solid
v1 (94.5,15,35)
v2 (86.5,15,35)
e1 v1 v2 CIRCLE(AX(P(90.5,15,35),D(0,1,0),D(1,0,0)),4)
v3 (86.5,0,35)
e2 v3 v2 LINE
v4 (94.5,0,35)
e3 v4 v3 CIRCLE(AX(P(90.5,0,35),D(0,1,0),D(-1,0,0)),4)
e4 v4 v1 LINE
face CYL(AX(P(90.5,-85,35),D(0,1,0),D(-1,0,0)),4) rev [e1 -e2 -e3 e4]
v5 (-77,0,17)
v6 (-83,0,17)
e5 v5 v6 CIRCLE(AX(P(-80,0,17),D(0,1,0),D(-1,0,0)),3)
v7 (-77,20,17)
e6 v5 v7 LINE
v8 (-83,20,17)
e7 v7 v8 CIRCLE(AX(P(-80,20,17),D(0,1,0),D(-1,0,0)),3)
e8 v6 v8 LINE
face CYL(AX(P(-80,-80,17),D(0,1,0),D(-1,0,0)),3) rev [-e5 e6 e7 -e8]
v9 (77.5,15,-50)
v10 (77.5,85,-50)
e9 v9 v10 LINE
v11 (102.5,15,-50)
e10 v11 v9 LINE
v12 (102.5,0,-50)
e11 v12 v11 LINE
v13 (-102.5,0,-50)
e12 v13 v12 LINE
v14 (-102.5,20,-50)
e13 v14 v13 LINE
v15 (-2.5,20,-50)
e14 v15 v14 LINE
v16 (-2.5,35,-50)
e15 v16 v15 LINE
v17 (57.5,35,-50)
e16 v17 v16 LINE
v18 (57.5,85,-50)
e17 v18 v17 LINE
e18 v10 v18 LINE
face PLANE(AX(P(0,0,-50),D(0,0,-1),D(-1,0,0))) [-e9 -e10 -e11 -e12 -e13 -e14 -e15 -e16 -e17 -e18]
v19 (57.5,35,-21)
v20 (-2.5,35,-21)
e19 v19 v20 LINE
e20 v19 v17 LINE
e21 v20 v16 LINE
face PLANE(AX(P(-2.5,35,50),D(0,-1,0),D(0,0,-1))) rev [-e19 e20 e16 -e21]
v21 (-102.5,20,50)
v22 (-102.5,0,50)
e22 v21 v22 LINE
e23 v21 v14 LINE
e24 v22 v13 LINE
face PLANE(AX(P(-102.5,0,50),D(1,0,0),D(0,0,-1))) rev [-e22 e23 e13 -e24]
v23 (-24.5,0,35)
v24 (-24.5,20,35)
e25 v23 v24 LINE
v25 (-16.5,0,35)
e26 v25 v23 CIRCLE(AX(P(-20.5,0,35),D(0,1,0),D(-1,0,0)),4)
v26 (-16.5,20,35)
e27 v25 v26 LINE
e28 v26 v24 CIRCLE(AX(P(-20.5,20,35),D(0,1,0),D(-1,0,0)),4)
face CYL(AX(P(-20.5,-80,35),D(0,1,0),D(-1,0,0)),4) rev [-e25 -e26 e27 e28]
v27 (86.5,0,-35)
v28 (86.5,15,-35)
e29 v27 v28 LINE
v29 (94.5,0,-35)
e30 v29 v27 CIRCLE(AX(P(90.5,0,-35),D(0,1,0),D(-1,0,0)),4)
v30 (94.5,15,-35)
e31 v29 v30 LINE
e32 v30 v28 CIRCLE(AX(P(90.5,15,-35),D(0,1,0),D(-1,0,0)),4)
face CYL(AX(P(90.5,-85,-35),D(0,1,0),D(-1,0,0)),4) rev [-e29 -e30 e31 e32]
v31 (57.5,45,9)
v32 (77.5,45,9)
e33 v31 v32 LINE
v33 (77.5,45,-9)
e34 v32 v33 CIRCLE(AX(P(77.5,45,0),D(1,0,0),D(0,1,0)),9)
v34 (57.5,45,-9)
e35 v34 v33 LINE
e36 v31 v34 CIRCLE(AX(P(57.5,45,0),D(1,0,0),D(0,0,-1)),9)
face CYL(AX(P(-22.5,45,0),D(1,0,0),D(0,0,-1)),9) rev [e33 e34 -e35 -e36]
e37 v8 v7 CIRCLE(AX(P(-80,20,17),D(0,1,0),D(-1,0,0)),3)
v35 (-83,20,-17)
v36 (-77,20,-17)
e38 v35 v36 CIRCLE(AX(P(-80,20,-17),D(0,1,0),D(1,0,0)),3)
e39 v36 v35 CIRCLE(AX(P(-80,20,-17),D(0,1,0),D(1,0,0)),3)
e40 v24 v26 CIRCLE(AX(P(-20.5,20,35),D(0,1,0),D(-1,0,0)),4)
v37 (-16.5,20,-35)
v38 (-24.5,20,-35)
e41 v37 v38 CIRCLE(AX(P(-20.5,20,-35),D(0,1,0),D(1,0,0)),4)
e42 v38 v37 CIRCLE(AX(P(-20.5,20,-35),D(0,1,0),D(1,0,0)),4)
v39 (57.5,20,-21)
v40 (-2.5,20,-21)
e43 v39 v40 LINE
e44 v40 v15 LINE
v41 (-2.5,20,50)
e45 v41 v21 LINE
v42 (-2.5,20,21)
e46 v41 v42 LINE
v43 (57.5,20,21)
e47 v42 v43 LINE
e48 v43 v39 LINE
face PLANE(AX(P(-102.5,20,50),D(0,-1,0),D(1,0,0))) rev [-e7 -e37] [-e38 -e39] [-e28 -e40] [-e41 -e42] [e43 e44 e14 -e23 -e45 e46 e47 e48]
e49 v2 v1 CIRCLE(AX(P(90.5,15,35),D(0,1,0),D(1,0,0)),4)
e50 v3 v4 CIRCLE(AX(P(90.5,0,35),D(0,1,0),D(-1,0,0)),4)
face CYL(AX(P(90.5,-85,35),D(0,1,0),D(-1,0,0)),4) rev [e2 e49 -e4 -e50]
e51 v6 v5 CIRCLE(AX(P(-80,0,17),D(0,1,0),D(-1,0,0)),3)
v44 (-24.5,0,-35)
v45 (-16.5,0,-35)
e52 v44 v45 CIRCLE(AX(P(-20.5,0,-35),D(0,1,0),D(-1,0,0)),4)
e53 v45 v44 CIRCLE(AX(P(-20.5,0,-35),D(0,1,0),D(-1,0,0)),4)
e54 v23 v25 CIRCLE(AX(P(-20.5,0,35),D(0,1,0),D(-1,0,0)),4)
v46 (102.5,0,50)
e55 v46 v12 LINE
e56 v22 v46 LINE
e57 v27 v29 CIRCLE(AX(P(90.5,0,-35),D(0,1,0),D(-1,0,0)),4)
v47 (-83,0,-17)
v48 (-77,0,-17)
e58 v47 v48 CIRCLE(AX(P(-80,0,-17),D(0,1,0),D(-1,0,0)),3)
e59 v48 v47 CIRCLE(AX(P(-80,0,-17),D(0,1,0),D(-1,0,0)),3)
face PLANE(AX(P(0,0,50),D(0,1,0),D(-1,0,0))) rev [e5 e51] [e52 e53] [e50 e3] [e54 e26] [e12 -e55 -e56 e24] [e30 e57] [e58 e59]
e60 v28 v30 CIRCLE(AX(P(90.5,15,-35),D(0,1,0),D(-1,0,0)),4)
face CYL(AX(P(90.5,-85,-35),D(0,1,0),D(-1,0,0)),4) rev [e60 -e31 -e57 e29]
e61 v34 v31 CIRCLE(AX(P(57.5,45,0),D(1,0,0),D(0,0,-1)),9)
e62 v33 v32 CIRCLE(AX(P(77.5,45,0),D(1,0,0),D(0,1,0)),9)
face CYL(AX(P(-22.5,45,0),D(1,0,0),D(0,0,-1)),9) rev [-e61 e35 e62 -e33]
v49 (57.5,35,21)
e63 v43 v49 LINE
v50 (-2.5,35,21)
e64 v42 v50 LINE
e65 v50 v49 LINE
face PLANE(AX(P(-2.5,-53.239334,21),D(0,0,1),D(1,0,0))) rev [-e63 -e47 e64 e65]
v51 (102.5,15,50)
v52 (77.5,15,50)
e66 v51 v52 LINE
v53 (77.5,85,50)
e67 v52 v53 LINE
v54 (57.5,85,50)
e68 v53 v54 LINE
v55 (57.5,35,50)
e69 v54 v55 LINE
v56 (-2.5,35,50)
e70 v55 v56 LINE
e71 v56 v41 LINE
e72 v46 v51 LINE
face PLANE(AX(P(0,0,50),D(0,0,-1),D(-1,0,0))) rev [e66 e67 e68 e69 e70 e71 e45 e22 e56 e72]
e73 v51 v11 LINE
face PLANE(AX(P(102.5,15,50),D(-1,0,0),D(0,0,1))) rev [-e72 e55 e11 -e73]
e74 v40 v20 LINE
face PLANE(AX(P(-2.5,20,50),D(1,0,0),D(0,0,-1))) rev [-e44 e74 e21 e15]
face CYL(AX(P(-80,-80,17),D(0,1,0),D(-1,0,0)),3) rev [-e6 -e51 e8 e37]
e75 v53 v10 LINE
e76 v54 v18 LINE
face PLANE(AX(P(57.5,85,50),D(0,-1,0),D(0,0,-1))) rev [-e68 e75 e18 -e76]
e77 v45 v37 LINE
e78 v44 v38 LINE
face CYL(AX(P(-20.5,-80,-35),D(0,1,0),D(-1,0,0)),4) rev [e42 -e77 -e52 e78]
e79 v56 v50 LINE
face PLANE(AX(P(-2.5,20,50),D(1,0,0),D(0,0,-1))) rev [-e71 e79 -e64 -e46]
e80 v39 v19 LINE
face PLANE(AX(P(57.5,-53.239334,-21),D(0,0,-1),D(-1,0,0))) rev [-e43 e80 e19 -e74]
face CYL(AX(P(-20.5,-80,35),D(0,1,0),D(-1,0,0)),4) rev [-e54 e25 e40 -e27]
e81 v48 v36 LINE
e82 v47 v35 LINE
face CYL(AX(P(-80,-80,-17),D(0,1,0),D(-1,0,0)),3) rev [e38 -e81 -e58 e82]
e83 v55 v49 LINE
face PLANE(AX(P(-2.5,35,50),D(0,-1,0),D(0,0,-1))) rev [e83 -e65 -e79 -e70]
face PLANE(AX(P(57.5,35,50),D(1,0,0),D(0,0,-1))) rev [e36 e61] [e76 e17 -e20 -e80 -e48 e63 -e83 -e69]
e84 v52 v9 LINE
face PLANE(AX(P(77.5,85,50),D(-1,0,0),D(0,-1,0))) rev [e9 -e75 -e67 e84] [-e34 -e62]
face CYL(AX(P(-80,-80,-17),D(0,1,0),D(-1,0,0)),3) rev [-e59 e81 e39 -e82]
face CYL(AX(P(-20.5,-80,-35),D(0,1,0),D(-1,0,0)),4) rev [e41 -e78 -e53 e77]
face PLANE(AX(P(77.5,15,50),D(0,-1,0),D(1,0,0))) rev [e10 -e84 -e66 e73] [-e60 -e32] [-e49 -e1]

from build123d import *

# Parameters (mm, degrees)
BRACKET_BODY_DEPTH          = 50
BASE_HOLES_8_SET_A_SKETCH_R = 4
BASE_HOLES_8_SET_A_DEPTH    = 100
STEP_NOTCH_SKETCH_W         = 60
STEP_NOTCH_SKETCH_H         = 42
STEP_NOTCH_DEPTH            = 15
WEB_BORE_18_SKETCH_R        = 9
WEB_BORE_18_DEPTH           = 100
BASE_HOLES_8_SET_B_SKETCH_R = 4
BASE_HOLES_8_SET_B_DEPTH    = 100
BASE_HOLES_6_SKETCH_R       = 3
BASE_HOLES_6_DEPTH          = 100


with BuildPart() as part:
    # Bracket Profile Sketch → Bracket Body (new, symmetric)
    with BuildSketch(Plane.XY):
        Polygon((0, 0), (-102.5, 0), (-102.5, 20), (-2.5, 20), (-2.5, 35), (57.5, 35), (57.5, 85), (77.5, 85), (77.5, 15), (102.5, 15), (102.5, 0), align=None)
    extrude(amount=BRACKET_BODY_DEPTH, both=True)

    # Base Holes Ø8 Set A Sketch → Base Holes Ø8 Set A (cut)
    with BuildSketch(Plane(origin=(0, 15, 0), x_dir=(1, 0, 0), z_dir=(0, 1, 0))):
        with Locations(Location((90.5, 35, 0), (0, 0, 180))):
            Circle(BASE_HOLES_8_SET_A_SKETCH_R)
        with Locations(Location((90.5, -35, 0), (0, 0, 180))):
            Circle(BASE_HOLES_8_SET_A_SKETCH_R)
    extrude(amount=-BASE_HOLES_8_SET_A_DEPTH, mode=Mode.SUBTRACT)

    # Step Notch Sketch → Step Notch (cut)
    with BuildSketch(Plane(origin=(0, 35, 0), x_dir=(1, 0, 0), z_dir=(0, 1, 0))):
        with Locations((27.5, 0)):
            Rectangle(STEP_NOTCH_SKETCH_W, STEP_NOTCH_SKETCH_H)
    extrude(amount=-STEP_NOTCH_DEPTH, mode=Mode.SUBTRACT)

    # Web Bore Ø18 Sketch → Web Bore Ø18 (cut)
    with BuildSketch(Plane(origin=(77.5, 0, 0), x_dir=(0, 0, -1), z_dir=(1, 0, 0))):
        with Locations((0, 45)):
            Circle(WEB_BORE_18_SKETCH_R)
    extrude(amount=-WEB_BORE_18_DEPTH, mode=Mode.SUBTRACT)

    # Base Holes Ø8 Set B Sketch → Base Holes Ø8 Set B (cut)
    with BuildSketch(Plane(origin=(0, 20, 0), x_dir=(1, 0, 0), z_dir=(0, 1, 0))):
        with Locations(Location((-20.5, -35, 0), (0, 0, 180))):
            Circle(BASE_HOLES_8_SET_B_SKETCH_R)
        with Locations(Location((-20.5, 35, 0), (0, 0, 180))):
            Circle(BASE_HOLES_8_SET_B_SKETCH_R)
    extrude(amount=-BASE_HOLES_8_SET_B_DEPTH, mode=Mode.SUBTRACT)

    # Base Holes Ø6 Sketch → Base Holes Ø6 (cut)
    with BuildSketch(Plane(origin=(0, 20, 0), x_dir=(1, 0, 0), z_dir=(0, 1, 0))):
        with Locations(Location((-80, -17, 0), (0, 0, 180))):
            Circle(BASE_HOLES_6_SKETCH_R)
        with Locations(Location((-80, 17, 0), (0, 0, 180))):
            Circle(BASE_HOLES_6_SKETCH_R)
    extrude(amount=-BASE_HOLES_6_DEPTH, mode=Mode.SUBTRACT)


solid = part.part
